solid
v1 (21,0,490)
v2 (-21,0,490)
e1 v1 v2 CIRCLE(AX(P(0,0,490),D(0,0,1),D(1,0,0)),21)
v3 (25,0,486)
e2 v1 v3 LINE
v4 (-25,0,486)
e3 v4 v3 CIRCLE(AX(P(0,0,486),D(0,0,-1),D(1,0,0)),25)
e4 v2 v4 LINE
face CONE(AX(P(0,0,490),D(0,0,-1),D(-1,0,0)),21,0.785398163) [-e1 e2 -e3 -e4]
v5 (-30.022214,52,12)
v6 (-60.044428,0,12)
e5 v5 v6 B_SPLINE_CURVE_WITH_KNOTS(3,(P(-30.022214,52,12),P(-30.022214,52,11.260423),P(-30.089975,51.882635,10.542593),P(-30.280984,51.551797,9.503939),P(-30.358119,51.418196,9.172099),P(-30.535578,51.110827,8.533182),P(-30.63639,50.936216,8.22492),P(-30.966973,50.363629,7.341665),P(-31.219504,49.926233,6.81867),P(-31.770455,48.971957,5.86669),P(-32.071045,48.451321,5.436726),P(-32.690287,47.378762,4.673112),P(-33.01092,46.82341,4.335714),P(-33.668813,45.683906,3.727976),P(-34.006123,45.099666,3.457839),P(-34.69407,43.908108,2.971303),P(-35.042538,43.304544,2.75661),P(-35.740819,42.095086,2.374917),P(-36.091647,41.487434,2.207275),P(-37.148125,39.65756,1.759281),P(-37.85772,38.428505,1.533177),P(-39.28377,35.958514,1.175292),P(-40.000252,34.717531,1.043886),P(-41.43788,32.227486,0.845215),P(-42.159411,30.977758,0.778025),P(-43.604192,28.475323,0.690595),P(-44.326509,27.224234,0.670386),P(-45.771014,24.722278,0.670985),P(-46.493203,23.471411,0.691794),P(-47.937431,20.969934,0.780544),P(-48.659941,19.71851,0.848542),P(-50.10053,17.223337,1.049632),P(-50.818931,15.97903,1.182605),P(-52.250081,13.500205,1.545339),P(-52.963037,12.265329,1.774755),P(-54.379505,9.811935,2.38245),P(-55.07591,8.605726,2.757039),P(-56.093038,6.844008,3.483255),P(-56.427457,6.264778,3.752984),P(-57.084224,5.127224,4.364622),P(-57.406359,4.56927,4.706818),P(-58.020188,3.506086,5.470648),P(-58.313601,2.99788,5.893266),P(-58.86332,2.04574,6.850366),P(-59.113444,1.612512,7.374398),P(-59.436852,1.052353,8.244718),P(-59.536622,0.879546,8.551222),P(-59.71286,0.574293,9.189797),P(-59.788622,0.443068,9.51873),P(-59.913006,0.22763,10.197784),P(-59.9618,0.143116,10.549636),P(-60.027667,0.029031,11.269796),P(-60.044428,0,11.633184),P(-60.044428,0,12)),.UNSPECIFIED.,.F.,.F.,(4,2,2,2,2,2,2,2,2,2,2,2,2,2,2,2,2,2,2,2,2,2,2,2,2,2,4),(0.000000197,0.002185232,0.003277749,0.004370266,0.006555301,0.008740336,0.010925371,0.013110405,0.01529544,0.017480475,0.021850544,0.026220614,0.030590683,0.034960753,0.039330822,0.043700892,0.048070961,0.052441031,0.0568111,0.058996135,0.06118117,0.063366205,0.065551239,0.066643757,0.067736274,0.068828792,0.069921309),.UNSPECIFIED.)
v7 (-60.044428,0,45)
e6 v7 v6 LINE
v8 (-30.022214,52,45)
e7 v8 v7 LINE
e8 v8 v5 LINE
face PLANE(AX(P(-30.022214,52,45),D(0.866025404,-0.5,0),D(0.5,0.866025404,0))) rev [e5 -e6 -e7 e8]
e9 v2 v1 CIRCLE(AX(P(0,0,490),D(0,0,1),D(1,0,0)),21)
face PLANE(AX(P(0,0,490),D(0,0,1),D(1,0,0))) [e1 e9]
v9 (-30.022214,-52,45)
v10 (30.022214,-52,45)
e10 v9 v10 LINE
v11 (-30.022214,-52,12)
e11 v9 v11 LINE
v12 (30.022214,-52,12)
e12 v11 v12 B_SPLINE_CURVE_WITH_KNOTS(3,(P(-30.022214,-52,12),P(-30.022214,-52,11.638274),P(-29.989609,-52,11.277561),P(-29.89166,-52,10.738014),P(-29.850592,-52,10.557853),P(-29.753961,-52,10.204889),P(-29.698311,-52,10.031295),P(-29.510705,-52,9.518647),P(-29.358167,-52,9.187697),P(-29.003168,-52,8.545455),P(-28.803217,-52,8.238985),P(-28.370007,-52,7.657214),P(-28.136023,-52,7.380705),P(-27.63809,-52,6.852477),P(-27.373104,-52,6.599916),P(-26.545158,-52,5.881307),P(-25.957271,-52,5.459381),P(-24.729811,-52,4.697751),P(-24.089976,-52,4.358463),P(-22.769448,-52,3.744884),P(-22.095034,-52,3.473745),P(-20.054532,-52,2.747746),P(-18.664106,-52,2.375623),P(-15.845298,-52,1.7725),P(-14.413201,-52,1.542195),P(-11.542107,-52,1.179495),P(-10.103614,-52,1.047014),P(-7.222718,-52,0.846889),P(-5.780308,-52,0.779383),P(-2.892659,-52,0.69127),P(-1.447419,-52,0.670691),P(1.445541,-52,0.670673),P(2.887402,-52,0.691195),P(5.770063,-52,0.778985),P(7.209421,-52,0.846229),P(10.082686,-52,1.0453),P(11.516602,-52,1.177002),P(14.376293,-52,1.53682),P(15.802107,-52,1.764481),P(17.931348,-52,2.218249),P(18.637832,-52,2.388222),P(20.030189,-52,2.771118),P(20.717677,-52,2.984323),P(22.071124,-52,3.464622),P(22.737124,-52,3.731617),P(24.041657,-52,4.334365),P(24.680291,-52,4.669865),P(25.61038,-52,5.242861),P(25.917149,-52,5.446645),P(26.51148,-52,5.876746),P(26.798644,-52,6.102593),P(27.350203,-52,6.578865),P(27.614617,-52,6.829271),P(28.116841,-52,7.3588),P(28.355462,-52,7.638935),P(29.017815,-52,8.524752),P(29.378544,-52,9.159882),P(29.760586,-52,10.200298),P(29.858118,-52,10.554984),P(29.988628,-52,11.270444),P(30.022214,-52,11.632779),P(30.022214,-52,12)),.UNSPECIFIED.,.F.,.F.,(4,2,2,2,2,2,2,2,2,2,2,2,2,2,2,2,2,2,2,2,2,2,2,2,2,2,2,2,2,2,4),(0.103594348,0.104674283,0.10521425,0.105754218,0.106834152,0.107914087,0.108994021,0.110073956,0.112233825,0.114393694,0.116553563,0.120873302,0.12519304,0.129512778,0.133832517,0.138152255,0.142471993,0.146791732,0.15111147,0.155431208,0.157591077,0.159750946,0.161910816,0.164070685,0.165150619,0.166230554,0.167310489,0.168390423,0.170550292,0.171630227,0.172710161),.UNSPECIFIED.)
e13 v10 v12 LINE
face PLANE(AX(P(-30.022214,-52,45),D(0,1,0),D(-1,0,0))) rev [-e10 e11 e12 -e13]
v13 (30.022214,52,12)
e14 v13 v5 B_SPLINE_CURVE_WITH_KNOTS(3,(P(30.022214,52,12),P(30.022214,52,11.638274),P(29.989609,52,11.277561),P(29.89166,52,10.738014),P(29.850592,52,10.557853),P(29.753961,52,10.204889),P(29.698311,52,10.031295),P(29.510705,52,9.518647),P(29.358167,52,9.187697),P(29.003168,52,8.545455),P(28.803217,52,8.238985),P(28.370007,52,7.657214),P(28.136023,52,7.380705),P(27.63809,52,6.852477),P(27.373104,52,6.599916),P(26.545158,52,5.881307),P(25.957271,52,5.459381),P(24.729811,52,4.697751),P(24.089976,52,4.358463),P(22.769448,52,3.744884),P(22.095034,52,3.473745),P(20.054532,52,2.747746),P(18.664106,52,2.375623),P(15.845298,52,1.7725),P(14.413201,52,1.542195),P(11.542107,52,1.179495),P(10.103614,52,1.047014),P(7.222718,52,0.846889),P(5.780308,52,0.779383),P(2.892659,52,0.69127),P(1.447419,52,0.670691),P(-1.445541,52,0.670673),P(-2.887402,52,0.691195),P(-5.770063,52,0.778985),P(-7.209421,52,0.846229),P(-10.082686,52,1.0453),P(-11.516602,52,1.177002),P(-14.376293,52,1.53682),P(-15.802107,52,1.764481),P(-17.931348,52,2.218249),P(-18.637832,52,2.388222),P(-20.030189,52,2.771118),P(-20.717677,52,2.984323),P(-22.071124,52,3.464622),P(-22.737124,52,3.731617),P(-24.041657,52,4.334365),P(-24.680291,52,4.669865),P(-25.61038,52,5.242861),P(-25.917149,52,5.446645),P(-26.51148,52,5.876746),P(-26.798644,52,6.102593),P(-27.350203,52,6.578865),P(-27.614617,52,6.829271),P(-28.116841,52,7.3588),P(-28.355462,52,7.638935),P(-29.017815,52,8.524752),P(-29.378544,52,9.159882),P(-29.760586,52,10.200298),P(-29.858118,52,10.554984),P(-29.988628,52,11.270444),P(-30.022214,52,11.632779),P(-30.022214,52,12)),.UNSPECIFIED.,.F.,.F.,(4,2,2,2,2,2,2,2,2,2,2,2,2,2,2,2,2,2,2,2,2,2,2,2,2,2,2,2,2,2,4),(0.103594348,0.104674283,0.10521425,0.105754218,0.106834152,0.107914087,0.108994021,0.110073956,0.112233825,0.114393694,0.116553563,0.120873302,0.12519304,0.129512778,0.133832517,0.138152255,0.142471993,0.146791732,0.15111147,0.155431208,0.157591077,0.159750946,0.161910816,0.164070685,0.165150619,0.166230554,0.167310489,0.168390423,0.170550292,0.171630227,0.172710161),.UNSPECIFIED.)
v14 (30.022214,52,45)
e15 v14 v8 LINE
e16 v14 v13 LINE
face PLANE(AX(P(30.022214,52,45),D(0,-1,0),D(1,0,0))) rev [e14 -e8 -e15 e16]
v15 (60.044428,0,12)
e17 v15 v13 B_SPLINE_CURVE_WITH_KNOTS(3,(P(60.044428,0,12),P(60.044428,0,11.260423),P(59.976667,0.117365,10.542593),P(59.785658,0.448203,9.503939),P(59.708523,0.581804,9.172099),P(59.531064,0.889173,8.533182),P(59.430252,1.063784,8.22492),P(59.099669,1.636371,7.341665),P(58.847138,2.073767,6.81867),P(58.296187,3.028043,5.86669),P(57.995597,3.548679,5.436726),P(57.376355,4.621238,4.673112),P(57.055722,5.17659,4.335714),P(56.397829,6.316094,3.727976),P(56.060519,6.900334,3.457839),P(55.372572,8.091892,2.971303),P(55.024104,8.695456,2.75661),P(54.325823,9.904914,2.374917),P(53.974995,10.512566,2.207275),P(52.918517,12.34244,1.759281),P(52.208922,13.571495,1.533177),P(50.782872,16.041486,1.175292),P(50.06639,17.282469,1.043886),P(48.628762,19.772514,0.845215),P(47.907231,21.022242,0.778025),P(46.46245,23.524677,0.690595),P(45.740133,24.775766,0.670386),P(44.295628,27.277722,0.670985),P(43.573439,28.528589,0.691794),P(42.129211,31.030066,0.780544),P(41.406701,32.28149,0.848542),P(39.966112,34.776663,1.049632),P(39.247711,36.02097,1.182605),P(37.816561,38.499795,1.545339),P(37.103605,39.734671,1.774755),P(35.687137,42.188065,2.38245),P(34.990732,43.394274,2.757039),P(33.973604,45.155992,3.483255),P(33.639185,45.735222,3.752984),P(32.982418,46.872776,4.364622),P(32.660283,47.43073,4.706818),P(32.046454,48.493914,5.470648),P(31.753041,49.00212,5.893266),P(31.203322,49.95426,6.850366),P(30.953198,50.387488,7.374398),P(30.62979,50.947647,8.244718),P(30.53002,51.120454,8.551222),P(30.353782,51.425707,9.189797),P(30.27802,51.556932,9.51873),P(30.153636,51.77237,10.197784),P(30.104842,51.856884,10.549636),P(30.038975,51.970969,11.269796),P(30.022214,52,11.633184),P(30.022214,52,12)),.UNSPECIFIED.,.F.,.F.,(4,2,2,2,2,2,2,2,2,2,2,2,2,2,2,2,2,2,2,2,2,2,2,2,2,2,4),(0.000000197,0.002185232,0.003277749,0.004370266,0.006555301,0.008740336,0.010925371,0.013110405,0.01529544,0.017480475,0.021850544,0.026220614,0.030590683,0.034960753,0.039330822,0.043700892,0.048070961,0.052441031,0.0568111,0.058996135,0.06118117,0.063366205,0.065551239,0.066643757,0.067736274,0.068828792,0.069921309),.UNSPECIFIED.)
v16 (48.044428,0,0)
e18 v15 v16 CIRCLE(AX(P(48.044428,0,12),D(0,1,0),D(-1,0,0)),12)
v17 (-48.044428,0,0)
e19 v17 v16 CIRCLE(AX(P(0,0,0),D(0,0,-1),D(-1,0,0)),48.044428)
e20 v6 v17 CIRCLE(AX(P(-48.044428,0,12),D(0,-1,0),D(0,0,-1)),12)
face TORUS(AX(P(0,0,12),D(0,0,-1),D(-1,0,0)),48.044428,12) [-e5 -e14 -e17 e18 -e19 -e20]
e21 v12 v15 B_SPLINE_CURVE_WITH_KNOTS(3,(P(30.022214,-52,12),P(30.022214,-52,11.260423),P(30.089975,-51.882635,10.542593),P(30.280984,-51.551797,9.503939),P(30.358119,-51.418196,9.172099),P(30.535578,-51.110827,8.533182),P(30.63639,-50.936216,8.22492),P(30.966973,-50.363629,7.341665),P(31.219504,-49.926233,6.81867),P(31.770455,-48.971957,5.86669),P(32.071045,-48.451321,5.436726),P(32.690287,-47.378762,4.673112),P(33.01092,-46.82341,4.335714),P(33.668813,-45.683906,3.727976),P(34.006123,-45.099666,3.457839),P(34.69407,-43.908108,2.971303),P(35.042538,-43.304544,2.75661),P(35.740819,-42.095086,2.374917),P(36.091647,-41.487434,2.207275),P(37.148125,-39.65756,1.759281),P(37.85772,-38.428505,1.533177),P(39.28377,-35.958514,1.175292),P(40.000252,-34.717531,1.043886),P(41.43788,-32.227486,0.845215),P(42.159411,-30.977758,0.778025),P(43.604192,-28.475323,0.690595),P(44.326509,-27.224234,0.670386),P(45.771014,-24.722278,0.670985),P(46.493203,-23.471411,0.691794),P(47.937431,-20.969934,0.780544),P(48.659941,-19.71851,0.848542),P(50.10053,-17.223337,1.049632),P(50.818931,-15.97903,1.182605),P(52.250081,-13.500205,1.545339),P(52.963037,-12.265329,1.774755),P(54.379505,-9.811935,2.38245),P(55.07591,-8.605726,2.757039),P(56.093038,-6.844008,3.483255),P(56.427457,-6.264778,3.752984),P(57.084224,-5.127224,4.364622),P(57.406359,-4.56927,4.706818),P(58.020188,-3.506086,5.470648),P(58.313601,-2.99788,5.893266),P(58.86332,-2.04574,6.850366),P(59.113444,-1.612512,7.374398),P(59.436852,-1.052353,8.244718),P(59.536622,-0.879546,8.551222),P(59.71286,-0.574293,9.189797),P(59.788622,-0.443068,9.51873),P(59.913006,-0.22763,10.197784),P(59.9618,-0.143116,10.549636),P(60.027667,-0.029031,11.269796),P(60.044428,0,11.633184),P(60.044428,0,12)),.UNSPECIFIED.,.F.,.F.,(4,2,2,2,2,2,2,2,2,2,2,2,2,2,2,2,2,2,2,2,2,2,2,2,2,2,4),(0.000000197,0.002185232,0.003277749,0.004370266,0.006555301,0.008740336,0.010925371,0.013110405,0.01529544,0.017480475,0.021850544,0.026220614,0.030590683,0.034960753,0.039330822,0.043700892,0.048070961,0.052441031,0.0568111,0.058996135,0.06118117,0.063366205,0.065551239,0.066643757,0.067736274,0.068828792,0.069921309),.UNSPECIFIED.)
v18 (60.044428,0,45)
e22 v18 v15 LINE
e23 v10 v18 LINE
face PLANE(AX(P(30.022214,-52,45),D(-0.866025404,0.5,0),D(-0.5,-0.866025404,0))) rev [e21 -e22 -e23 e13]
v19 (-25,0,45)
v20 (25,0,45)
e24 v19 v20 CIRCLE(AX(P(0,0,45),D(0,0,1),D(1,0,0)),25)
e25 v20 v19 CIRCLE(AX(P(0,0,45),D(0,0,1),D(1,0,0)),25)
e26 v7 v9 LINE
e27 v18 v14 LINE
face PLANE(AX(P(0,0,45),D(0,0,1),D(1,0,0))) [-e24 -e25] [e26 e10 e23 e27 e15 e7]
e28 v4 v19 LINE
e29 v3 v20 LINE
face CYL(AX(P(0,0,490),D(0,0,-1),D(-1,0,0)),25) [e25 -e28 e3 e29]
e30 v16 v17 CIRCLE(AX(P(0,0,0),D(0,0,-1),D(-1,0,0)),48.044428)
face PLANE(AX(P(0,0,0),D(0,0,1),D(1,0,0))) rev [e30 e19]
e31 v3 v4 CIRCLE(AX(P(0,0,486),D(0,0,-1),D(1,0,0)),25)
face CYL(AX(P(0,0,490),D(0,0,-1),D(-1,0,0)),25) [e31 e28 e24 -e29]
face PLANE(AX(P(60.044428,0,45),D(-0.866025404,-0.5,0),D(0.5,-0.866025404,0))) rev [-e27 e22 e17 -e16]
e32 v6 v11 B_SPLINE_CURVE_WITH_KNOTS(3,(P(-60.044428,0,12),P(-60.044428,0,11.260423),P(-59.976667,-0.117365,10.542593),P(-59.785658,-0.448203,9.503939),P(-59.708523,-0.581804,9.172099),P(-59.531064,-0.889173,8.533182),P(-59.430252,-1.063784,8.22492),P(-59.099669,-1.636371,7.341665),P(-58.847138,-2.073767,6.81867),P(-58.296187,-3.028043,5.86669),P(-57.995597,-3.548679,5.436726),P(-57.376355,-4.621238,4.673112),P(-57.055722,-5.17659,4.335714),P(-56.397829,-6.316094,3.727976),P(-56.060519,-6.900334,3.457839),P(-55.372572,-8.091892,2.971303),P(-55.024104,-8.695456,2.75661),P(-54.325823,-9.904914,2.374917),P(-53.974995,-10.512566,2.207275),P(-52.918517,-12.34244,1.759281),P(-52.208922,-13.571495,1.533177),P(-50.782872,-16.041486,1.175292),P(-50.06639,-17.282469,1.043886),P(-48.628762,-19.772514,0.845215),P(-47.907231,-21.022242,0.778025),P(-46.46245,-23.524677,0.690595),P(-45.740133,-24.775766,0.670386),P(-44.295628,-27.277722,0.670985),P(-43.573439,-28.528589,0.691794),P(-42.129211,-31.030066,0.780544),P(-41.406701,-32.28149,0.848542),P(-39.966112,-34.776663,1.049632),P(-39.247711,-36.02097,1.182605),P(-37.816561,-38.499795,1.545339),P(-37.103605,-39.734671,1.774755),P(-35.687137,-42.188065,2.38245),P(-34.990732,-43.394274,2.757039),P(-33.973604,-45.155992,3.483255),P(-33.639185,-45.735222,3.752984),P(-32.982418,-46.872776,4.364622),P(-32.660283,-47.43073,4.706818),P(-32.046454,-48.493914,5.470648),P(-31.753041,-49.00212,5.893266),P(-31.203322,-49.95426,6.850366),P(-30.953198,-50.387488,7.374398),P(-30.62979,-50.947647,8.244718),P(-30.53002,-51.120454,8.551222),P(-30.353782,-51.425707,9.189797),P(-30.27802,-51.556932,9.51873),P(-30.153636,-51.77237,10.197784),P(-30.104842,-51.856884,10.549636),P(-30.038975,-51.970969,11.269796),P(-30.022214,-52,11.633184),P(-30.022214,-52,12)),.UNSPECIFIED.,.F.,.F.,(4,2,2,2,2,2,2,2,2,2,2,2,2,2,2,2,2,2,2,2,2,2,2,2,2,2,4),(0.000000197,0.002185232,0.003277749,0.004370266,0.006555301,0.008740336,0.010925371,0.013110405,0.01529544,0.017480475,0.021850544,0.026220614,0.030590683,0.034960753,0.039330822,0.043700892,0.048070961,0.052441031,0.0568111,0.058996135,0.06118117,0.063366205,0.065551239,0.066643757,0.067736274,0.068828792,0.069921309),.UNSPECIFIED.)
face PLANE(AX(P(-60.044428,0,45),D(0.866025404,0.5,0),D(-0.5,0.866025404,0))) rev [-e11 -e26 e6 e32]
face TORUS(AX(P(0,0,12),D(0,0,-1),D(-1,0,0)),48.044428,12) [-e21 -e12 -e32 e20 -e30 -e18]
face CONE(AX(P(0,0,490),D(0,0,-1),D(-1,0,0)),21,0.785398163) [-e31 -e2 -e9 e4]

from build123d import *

# Parameters (mm, degrees)
BOSS_EXTRUDE1_DEPTH = 45
SKETCH4_R           = 25
BOSS_EXTRUDE2_DEPTH = 445
CHAMFER2_SIZE       = 4


with BuildPart() as part:
    # Sketch1 → Boss-Extrude1 (new body)
    with BuildSketch(Plane.XY):
        Polygon((30.022213998, -52), (60.044427996, 0), (30.022213998, 52), (-30.022213998, 52), (-60.044427996, 0), (-30.022213998, -52), align=None)
    extrude(amount=BOSS_EXTRUDE1_DEPTH)

    # Sketch3 → Cut-Revolve3 (revolve, cut)
    with BuildSketch(Plane(origin=(0, 0, 0), x_dir=(1, 0, 0), z_dir=(0, 1, 0))):
        with BuildLine():
            Line((-60.044427996, -12), (-60.044427996, 0))
            Line((-60.044427996, 0), (-48.044427996, 0))
            ThreePointArc((-48.044427996, 0), (-56.52970937, -3.514718626), (-60.044427996, -12))
        make_face()
    revolve(axis=Axis((0, 0, -19.888042613), (0, 0, 1)), mode=Mode.SUBTRACT)

    # Sketch4 → Boss-Extrude2 (add)
    with BuildSketch(Plane.XY.offset(45)):
        Circle(SKETCH4_R)
    extrude(amount=BOSS_EXTRUDE2_DEPTH)

    # Chamfer2
    chamfer2_edges = [part.edges().sort_by_distance(p)[0] for p in [
        (-25, 0, 490),
    ]]
    chamfer(chamfer2_edges, length=CHAMFER2_SIZE)


solid = part.part
